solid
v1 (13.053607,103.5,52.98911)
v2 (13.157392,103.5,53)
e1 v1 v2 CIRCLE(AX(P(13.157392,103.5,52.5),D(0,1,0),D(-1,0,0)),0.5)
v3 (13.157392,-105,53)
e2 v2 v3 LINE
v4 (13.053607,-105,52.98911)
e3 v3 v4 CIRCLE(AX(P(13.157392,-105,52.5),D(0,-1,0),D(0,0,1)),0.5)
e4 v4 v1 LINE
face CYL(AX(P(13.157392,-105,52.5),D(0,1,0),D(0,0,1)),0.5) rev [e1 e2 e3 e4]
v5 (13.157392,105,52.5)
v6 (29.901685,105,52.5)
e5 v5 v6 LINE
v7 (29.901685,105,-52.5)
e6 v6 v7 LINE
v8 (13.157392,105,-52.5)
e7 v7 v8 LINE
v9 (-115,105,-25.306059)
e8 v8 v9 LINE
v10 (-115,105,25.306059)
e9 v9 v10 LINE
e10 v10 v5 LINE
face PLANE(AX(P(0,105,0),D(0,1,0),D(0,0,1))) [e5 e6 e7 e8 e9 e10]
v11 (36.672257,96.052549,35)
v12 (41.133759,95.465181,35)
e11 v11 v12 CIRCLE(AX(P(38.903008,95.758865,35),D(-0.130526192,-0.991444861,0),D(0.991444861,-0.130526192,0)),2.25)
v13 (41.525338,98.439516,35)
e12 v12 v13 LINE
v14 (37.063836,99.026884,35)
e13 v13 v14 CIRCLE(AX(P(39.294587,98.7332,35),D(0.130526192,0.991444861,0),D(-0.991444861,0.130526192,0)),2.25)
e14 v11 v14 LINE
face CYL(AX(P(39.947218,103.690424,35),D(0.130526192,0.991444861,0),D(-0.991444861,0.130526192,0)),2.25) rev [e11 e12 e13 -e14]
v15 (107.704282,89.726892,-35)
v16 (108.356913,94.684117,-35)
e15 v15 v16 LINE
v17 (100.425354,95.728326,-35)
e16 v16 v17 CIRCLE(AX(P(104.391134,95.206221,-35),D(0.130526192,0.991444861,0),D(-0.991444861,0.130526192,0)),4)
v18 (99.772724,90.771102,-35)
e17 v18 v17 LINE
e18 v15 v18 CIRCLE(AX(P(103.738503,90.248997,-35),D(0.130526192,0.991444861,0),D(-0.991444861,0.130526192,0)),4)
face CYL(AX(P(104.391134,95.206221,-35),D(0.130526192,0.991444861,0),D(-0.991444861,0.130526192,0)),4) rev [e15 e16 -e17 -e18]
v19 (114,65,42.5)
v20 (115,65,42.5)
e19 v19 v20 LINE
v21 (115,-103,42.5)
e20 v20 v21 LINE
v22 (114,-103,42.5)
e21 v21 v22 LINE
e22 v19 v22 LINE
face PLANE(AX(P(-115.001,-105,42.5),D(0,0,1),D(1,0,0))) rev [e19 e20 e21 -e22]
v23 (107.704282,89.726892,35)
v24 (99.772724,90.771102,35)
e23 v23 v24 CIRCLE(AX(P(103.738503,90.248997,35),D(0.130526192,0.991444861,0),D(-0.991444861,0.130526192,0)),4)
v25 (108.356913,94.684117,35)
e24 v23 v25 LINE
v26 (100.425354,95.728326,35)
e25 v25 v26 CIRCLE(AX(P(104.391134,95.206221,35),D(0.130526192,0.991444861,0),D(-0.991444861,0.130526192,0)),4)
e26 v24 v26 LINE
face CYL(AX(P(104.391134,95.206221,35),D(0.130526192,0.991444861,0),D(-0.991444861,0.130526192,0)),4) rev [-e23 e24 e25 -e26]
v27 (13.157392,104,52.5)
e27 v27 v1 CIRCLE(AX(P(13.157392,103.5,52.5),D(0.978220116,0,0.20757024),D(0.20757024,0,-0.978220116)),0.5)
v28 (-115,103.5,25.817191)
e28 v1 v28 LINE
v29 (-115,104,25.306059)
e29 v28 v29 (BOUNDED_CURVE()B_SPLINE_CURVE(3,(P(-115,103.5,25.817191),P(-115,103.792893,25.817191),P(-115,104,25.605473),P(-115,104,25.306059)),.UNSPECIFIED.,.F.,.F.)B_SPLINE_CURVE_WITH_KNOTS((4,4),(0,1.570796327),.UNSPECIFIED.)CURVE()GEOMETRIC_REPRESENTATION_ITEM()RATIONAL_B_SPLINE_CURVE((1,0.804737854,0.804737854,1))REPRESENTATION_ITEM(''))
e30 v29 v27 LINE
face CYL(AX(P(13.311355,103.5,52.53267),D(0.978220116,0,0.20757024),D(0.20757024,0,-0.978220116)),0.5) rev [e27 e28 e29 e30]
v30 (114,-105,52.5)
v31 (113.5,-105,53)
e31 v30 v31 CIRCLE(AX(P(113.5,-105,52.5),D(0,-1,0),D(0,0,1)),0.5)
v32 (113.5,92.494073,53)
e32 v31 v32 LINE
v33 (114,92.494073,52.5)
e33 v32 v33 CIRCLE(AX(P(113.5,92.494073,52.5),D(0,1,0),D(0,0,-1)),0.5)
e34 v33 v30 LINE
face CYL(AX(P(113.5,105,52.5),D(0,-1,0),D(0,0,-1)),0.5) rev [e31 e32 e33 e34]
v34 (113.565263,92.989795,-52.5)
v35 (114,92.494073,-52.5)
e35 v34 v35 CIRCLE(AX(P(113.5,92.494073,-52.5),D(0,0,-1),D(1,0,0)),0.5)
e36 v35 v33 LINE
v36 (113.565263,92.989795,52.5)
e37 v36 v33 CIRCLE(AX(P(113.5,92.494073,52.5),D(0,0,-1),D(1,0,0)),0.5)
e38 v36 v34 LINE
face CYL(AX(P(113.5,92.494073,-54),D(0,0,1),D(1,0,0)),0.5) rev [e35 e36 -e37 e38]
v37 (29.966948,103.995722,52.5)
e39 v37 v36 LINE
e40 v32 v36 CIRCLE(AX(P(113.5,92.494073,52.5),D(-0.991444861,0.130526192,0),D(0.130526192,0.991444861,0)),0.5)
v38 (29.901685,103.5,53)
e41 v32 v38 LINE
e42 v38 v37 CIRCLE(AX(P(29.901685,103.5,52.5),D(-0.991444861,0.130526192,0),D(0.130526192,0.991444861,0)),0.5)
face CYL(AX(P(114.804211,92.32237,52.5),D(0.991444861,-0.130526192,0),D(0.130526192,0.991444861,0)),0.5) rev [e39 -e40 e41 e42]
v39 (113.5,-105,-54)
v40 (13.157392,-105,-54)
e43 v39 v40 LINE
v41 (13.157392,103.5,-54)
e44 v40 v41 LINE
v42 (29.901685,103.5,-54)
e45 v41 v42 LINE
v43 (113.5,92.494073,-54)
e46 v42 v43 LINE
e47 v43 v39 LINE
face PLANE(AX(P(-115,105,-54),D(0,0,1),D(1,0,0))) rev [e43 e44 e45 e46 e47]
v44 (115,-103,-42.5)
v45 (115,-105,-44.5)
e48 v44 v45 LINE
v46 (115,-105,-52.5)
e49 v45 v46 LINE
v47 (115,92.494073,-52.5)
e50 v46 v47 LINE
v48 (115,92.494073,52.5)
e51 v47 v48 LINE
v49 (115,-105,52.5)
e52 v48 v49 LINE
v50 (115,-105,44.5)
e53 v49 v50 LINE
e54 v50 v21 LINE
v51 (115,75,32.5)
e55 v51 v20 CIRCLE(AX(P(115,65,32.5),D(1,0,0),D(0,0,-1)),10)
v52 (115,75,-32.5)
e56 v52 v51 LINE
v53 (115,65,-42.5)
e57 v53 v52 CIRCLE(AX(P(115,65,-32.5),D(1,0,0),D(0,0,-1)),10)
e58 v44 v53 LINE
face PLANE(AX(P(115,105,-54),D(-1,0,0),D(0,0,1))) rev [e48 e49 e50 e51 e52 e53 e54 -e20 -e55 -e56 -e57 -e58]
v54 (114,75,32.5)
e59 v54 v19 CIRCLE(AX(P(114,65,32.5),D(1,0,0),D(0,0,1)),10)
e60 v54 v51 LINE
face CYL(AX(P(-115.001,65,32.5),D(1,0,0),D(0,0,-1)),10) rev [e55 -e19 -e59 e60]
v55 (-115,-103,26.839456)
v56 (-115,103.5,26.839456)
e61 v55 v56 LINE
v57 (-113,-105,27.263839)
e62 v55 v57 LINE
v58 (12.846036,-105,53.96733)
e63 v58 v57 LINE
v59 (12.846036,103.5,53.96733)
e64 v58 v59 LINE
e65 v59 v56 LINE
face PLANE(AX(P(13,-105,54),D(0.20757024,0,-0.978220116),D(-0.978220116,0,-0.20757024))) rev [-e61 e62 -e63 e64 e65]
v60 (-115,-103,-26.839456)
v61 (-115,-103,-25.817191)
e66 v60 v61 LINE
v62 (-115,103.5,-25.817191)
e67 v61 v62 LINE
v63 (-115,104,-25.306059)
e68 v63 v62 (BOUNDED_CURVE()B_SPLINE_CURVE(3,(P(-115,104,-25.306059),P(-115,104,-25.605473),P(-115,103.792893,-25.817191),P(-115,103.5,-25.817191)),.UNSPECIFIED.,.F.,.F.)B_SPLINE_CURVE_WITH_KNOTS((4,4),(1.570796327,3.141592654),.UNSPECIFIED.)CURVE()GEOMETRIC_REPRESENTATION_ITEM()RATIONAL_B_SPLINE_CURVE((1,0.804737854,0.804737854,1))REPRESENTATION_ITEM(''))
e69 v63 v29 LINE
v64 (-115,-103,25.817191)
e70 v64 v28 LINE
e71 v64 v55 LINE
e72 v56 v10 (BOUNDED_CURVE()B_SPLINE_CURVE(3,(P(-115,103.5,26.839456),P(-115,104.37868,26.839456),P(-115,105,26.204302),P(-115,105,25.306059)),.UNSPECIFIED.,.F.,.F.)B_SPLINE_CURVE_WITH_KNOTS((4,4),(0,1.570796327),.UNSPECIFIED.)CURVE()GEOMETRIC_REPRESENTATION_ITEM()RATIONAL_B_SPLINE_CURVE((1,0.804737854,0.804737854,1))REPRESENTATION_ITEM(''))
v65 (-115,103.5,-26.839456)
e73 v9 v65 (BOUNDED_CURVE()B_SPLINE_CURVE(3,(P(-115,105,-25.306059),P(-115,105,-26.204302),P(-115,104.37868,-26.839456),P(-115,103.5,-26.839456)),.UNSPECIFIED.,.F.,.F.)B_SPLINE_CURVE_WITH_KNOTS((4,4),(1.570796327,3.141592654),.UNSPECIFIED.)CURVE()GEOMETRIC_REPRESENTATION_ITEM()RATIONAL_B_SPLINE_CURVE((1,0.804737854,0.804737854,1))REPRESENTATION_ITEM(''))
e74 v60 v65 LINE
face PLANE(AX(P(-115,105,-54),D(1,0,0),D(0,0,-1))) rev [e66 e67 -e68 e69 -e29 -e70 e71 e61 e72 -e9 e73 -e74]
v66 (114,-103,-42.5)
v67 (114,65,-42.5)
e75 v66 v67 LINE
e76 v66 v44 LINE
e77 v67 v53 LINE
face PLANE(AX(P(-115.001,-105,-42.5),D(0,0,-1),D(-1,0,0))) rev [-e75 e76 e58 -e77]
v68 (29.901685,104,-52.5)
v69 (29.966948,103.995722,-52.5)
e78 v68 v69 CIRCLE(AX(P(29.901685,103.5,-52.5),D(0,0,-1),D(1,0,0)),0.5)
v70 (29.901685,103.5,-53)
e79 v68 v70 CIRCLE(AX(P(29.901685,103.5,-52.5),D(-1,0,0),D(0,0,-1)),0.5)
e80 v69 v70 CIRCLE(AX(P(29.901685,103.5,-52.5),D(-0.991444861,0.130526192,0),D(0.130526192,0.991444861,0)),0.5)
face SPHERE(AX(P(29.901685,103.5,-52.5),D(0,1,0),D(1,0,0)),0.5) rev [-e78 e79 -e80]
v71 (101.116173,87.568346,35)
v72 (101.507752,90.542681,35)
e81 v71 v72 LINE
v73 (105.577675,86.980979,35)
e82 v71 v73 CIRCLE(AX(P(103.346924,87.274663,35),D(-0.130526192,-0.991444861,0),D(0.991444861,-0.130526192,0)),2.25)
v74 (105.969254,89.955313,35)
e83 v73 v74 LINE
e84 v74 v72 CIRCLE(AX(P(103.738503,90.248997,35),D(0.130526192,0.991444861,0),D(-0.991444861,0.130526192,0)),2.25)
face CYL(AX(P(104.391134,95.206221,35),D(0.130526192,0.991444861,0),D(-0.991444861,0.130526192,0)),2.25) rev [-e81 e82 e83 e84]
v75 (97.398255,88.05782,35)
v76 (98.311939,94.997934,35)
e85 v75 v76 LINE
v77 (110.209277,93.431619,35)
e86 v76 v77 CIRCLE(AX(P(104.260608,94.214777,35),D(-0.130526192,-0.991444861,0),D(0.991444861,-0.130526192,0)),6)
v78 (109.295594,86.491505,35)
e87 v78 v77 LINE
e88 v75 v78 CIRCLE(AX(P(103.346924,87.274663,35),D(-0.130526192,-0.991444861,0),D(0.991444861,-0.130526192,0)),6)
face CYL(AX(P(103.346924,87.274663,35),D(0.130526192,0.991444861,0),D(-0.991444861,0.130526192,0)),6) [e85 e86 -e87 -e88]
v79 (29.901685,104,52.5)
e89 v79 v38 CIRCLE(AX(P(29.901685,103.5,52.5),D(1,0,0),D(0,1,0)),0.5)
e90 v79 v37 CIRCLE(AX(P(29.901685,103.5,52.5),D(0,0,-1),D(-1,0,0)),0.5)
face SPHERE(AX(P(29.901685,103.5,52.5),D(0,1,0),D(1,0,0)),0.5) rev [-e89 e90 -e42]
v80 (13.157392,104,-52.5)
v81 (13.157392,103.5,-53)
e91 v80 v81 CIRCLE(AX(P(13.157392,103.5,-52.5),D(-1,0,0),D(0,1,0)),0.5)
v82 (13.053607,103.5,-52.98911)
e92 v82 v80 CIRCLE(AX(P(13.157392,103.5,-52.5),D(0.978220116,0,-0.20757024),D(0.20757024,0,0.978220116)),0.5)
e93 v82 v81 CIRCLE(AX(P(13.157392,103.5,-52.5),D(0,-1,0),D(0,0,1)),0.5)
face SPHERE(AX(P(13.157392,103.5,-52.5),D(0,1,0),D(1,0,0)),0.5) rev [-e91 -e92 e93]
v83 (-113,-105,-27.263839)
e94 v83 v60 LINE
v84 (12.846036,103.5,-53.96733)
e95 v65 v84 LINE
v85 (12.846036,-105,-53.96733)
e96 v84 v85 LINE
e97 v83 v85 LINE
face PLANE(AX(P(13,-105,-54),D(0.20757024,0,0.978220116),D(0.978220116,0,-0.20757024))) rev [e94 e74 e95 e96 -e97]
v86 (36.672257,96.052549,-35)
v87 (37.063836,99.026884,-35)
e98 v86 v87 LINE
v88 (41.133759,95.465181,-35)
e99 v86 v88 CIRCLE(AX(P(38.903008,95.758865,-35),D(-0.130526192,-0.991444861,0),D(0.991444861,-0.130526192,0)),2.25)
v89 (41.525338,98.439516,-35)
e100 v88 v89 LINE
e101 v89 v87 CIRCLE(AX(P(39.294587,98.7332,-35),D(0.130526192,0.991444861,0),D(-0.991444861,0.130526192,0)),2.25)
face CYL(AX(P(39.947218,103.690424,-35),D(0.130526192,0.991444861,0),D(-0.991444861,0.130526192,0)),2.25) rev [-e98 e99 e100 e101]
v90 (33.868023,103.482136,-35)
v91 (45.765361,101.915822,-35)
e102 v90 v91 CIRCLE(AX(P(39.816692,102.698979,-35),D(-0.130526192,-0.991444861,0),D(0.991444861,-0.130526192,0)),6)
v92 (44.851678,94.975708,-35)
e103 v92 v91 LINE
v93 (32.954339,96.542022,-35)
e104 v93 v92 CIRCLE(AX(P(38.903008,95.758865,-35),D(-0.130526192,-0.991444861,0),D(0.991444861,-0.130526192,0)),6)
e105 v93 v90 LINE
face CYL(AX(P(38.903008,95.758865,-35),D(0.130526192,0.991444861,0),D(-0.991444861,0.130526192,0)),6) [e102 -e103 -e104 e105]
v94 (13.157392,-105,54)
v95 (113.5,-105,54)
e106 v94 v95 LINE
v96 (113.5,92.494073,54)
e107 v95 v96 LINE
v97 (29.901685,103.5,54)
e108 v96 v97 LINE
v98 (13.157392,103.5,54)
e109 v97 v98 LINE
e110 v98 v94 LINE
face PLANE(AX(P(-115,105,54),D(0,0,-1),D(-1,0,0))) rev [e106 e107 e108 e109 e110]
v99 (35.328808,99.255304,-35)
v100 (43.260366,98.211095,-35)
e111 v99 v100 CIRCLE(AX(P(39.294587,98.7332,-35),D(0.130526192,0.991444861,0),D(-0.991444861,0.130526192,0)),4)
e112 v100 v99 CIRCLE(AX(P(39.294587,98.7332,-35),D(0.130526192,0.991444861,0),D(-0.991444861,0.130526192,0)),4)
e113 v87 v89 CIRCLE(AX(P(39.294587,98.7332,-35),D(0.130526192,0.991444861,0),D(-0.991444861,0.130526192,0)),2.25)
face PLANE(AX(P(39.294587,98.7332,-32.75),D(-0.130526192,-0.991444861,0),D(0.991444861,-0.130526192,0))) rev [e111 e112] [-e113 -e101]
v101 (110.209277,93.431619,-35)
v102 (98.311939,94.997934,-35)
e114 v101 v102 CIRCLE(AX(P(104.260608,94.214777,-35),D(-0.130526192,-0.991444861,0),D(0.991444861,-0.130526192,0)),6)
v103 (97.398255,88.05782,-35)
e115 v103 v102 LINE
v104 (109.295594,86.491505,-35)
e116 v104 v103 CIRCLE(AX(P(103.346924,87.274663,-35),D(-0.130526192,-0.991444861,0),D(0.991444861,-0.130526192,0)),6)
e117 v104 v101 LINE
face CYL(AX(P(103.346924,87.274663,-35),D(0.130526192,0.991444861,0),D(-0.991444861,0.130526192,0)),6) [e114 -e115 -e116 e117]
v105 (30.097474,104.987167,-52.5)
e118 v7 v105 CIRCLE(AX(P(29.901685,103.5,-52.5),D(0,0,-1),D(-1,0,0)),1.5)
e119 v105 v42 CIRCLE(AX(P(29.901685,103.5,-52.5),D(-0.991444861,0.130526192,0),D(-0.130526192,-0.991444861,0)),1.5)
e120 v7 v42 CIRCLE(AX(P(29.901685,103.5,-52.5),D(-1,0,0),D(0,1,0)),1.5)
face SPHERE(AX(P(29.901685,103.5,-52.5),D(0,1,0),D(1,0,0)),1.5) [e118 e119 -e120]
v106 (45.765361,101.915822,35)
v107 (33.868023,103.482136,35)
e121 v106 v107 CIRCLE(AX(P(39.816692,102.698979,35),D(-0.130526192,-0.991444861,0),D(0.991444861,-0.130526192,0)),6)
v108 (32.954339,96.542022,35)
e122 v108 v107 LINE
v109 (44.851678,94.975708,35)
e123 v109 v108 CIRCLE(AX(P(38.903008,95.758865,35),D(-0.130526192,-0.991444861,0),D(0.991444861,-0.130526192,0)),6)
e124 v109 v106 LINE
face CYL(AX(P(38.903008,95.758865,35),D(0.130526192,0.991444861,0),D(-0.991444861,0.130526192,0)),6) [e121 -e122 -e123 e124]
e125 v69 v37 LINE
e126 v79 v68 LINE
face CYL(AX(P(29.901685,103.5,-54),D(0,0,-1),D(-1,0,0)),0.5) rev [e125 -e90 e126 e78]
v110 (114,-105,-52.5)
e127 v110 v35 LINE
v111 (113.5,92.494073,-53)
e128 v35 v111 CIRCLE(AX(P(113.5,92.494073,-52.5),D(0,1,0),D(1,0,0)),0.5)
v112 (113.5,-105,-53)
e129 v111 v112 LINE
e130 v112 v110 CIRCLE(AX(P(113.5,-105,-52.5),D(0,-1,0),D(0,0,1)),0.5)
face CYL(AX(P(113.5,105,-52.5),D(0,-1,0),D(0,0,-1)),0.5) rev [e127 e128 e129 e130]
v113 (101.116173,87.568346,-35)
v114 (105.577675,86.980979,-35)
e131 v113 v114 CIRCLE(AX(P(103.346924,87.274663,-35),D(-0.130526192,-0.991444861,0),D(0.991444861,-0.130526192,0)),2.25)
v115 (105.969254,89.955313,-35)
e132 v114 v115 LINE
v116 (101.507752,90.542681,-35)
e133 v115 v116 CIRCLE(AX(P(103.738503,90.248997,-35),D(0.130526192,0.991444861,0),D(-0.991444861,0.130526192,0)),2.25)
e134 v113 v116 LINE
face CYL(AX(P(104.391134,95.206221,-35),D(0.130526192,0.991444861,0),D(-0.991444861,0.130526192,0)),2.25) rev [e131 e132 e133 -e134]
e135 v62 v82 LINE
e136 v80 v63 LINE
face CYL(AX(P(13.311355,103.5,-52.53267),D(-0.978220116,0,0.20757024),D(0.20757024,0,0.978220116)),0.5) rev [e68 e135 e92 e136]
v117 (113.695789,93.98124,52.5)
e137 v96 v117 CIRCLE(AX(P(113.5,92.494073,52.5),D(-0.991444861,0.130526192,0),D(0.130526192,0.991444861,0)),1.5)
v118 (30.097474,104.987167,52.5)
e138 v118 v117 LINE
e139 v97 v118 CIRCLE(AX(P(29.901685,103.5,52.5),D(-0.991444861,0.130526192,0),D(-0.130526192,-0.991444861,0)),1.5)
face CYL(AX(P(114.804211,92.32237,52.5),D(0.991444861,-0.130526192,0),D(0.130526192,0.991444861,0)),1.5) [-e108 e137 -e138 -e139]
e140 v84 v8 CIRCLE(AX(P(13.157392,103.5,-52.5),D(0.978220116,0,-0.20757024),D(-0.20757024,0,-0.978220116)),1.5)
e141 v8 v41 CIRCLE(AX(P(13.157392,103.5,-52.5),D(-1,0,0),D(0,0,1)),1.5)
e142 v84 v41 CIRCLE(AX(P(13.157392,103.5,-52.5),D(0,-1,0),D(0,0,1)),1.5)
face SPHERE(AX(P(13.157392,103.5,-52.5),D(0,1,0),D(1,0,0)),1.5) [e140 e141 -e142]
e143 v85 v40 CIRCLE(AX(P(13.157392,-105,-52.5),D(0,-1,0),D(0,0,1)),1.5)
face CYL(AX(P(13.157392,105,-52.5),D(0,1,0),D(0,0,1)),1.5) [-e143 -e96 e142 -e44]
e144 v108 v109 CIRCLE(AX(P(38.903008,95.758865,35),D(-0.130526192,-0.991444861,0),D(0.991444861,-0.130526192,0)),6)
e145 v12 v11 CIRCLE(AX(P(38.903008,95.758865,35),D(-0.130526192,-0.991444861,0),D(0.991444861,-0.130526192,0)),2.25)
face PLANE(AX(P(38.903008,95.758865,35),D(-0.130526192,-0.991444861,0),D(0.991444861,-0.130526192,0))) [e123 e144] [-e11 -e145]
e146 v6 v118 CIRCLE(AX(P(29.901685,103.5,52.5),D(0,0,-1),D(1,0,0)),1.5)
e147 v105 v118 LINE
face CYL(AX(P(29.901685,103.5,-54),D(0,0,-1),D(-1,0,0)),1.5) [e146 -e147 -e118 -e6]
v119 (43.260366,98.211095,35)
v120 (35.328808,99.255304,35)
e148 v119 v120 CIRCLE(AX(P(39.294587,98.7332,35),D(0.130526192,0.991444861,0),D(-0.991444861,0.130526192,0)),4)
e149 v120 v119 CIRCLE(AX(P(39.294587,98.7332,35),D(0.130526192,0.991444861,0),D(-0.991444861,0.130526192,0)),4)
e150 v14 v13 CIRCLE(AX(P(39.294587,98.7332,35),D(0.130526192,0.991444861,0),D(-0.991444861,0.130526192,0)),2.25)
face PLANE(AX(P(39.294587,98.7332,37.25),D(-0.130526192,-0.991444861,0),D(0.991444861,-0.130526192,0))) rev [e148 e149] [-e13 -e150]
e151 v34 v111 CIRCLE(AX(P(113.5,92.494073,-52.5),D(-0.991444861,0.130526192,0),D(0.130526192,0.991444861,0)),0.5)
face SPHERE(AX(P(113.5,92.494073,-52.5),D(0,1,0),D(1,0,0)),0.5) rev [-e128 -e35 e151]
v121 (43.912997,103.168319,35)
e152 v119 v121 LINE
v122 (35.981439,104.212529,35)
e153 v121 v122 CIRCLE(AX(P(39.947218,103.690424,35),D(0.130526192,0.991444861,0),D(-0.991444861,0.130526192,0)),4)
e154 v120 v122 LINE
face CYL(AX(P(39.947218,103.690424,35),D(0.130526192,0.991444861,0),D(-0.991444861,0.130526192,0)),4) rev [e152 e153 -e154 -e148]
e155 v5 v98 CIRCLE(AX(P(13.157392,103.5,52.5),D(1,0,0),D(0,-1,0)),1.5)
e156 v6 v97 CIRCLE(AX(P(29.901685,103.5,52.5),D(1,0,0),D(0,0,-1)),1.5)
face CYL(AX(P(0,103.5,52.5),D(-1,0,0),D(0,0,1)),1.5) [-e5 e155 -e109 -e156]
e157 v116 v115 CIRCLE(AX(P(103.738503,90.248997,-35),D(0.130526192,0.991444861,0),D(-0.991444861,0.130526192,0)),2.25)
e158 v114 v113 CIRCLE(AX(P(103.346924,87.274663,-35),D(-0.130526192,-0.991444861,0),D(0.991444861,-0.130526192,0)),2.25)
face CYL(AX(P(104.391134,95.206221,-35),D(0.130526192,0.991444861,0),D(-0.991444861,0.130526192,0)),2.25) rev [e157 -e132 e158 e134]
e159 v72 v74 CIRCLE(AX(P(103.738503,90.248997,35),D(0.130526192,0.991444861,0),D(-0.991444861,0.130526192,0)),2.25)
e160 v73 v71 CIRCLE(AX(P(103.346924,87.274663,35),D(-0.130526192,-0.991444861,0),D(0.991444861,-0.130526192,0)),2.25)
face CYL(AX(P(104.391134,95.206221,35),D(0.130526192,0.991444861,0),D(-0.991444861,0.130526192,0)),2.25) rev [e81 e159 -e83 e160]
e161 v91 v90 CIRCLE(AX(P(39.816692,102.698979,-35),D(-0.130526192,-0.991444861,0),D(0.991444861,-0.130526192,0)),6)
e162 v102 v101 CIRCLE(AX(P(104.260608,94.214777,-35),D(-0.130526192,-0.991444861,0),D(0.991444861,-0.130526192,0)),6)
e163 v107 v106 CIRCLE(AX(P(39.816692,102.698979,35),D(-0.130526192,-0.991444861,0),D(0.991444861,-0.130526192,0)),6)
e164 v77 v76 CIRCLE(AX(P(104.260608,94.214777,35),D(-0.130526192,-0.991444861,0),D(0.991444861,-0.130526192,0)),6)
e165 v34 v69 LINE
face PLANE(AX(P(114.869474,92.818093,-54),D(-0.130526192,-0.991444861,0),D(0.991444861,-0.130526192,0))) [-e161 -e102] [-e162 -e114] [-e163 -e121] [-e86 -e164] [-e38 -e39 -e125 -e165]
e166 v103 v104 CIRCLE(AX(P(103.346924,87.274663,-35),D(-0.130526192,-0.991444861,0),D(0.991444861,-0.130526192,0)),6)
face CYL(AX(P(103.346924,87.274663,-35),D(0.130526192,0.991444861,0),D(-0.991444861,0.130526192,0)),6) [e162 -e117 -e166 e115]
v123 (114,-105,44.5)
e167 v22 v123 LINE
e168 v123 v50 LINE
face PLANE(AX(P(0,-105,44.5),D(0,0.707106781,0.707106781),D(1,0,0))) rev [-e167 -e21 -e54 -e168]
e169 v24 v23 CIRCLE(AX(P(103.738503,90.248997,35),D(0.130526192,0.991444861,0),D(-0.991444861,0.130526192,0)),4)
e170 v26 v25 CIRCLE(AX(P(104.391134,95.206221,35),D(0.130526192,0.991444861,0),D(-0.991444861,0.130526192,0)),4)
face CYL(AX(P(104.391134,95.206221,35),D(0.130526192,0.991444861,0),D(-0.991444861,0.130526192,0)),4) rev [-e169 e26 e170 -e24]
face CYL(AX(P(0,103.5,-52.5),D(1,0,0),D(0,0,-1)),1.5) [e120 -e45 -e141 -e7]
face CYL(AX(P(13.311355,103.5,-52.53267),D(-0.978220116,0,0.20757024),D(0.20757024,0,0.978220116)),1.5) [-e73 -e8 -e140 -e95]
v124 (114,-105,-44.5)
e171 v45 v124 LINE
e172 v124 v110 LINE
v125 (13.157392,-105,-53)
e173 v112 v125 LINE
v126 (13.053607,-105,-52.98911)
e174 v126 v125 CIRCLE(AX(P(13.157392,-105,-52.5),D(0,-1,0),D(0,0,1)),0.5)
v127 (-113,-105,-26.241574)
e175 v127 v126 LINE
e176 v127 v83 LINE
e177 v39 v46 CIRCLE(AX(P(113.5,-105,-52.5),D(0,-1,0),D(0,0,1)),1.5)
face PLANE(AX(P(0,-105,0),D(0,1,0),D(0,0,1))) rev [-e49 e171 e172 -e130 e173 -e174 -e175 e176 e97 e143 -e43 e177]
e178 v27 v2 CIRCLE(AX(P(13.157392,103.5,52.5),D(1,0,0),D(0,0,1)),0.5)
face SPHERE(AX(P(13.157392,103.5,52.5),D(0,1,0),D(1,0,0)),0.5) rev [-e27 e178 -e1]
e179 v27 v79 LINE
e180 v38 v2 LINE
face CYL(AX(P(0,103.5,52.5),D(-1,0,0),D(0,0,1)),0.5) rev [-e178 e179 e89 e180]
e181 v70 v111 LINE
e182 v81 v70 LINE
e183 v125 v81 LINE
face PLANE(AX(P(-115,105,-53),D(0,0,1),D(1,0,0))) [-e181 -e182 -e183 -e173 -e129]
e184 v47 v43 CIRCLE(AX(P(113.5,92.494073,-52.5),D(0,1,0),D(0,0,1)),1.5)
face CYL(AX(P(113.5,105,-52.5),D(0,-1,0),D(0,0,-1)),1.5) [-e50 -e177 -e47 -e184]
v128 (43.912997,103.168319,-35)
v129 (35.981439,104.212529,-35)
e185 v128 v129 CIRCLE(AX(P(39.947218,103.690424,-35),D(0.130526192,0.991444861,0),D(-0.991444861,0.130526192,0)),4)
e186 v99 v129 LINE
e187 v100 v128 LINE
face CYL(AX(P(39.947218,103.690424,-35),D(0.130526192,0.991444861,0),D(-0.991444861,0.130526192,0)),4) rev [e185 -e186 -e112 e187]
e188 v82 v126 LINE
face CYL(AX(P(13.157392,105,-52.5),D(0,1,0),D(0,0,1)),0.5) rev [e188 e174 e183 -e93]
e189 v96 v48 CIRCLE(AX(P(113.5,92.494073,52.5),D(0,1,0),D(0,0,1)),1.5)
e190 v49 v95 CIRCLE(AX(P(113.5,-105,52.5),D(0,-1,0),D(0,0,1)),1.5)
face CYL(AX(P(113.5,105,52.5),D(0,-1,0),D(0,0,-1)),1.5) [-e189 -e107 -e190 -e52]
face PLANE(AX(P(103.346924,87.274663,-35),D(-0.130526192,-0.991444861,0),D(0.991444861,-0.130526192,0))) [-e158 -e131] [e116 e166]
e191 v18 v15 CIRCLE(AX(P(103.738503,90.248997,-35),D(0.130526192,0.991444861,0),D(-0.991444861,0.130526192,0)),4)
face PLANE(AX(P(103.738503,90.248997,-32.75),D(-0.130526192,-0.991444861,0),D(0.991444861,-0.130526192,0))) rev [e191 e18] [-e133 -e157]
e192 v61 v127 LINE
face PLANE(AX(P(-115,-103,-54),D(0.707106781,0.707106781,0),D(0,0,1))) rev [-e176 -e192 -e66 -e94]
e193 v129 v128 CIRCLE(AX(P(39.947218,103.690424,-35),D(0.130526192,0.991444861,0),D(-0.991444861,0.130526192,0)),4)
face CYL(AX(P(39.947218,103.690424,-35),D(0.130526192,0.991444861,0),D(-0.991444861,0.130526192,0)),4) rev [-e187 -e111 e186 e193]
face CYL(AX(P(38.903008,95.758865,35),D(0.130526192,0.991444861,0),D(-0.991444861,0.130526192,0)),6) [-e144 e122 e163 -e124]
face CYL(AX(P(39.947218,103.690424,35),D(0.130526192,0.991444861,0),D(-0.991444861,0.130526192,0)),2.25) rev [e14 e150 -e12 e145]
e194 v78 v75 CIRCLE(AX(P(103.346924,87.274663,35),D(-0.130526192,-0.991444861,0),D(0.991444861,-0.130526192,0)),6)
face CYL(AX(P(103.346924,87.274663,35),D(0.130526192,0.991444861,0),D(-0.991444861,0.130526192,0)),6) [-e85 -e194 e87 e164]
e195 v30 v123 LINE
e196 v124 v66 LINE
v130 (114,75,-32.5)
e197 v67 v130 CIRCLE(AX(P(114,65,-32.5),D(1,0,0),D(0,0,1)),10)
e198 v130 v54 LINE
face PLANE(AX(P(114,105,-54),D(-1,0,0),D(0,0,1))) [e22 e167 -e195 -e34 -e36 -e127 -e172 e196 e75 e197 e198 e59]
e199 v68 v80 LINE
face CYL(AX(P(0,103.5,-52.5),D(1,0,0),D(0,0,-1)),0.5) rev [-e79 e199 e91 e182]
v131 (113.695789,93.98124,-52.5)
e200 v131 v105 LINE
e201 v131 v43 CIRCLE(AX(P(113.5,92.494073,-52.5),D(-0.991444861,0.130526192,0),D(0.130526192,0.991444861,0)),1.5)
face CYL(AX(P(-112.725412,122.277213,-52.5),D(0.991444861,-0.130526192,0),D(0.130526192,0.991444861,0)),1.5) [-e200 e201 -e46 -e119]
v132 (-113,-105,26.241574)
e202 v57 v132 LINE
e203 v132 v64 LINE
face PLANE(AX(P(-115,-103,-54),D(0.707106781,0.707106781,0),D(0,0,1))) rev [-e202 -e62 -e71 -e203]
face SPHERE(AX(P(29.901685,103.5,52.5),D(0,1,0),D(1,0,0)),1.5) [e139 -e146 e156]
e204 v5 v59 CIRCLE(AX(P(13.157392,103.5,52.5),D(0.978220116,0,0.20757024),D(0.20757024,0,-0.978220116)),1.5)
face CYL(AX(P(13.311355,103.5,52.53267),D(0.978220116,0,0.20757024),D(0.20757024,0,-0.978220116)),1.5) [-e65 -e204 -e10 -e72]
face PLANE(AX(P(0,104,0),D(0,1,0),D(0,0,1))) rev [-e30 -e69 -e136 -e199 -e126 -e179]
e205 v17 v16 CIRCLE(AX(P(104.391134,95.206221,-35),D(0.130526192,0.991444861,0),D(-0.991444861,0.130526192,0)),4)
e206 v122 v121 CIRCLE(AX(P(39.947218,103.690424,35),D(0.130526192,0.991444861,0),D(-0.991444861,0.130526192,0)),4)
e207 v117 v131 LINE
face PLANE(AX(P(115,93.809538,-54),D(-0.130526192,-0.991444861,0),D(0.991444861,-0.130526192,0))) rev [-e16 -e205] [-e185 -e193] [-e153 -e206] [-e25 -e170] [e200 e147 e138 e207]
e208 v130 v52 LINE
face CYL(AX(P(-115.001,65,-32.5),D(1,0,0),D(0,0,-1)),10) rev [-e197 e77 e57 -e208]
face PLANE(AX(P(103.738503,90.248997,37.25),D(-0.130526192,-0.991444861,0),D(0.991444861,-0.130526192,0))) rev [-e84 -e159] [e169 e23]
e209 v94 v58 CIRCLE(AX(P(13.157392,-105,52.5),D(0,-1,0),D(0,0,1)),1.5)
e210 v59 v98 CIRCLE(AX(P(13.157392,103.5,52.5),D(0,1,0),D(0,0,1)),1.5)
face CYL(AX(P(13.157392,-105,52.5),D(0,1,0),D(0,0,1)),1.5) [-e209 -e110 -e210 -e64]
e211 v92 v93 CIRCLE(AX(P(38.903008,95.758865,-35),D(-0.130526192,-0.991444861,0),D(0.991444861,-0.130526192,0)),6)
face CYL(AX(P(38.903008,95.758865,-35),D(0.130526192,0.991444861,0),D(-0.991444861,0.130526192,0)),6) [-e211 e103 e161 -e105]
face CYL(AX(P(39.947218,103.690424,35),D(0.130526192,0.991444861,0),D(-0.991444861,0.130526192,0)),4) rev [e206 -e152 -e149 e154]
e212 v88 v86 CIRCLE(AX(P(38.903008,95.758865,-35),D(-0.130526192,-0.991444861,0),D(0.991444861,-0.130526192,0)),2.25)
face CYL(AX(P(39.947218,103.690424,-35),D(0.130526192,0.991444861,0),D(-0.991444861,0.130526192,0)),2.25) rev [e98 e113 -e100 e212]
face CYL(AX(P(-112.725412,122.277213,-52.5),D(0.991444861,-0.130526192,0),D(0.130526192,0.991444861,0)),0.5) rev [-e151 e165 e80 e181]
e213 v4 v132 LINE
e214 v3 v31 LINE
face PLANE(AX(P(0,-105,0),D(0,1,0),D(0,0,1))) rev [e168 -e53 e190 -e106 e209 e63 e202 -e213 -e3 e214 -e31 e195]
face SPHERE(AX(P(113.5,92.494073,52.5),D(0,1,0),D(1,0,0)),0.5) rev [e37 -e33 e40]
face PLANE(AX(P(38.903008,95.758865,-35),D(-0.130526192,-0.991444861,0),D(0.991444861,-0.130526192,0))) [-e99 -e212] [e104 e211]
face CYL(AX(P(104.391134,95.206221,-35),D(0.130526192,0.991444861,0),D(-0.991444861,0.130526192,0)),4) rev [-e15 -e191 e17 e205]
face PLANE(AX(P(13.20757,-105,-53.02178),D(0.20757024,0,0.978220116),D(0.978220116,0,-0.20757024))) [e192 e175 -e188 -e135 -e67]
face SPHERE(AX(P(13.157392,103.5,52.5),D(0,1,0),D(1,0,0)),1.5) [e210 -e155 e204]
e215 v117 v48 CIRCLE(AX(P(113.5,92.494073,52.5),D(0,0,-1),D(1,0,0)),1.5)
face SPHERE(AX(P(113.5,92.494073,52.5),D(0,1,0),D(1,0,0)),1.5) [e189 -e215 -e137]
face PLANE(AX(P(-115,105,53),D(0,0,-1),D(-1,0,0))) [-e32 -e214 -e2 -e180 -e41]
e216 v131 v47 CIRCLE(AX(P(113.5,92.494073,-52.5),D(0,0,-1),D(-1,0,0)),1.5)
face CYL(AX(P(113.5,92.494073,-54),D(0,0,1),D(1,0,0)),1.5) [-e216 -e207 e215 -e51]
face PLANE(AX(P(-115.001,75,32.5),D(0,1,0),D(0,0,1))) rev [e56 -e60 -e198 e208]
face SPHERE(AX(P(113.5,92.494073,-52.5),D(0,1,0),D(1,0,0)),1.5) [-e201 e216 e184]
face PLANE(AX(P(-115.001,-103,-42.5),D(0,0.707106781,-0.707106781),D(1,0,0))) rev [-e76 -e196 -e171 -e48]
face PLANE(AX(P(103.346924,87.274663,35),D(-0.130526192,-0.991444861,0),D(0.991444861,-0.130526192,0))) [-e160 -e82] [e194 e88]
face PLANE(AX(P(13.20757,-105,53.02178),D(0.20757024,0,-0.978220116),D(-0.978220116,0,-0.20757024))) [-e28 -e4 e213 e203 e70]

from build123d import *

# Parameters (mm, degrees)
SKETCH1_W                                            = 230
SKETCH1_H                                            = 108
BOSS_EXTRUDE1_DEPTH                                  = 105
CUT_EXTRUDE1_DEPTH                                   = 246.440420469
CUT_EXTRUDE2_DEPTH                                   = 190.509894201
FILLET1_R                                            = 1.5
SHELL1_T                                             = -1
SKETCH4_R                                            = 6
BOSS_EXTRUDE2_DEPTH                                  = 7
HOLE_SIZE_PER_SOCKET_HEAD_CAP_SCREW_TYPE_D           = 4.5
HOLE_SIZE_PER_SOCKET_HEAD_CAP_SCREW_TYPE_CBORE_D     = 8
HOLE_SIZE_PER_SOCKET_HEAD_CAP_SCREW_TYPE_CBORE_DEPTH = 5
CUT_EXTRUDE3_REACH                                   = 260.536
CHAMFER1_SIZE                                        = 2


with BuildPart() as part:
    # Sketch1 → Boss-Extrude1 (new, symmetric)
    with BuildSketch(Plane(origin=(0, 0, 0), x_dir=(1, 0, 0), z_dir=(0, 1, 0))):
        Rectangle(SKETCH1_W, SKETCH1_H)
    extrude(amount=BOSS_EXTRUDE1_DEPTH, both=True)

    # Sketch2 → Cut-Extrude1 (cut, through all)
    with BuildSketch(Plane(origin=(0, 105, 0), x_dir=(1, 0, 0), z_dir=(0, 1, 0))):
        Polygon((-115, 26.839455747), (-115, 54), (13, 54), align=None)
        Polygon((-115, -26.839455747), (-115, -54), (13, -54), align=None)
    extrude(amount=-CUT_EXTRUDE1_DEPTH, mode=Mode.SUBTRACT)

    # Sketch3 → Cut-Extrude2 (cut, through all)
    with BuildSketch(Plane.XY.offset(54)):
        Polygon((30, 105), (115, 105), (115, 93.809537705), align=None)
    extrude(amount=-CUT_EXTRUDE2_DEPTH, mode=Mode.SUBTRACT)

    # Fillet1
    fillet1_edges = [part.edges().sort_by_distance(p)[0] for p in [
        (13, 0, -54),
        (-51, 105, -40.419727874),
        (21.5, 105, 54),
        (13, 0, 54),
        (-51, 105, 40.419727874),
        (21.5, 105, -54),
        (115, -5.595231147, 54),
        (115, -5.595231147, -54),
        (72.5, 99.404768853, -54),
        (115, 93.809537705, 0),
        (30, 105, 0),
        (72.5, 99.404768853, 54),
    ]]
    fillet(fillet1_edges, radius=FILLET1_R)

    # Shell1
    shell1_openings = [part.faces().sort_by_distance(p)[0] for p in [
        (11.766407096, -105, 0),
        (-115, -0.009166967, 0),
    ]]
    offset(amount=SHELL1_T, openings=shell1_openings, kind=Kind.INTERSECTION)

    # Sketch4 → Boss-Extrude2 (add)
    with BuildSketch(Plane(origin=(13.968586281, 106.101946695, 0), x_dir=(0.9914448613738114, -0.1305261922200448, 0), z_dir=(-0.1305261922200448, -0.9914448613738114, 0))):
        with Locations((26.071147756, 35)):
            Circle(SKETCH4_R)
        with Locations((26.071147756, -35)):
            Circle(SKETCH4_R)
        with Locations((91.071147756, -35)):
            Circle(SKETCH4_R)
        with Locations((91.071147756, 35)):
            Circle(SKETCH4_R)
    extrude(amount=BOSS_EXTRUDE2_DEPTH)

    # Hole size per socket head cap screw type1 (through all)
    with Locations(Plane(origin=(14.099112474, 107.093391557, 0), x_dir=(0.9914448613738114, -0.1305261922200448, 0), z_dir=(0.1305261922200448, 0.9914448613738114, 0))):
        with Locations((26.071147756, 35), (91.071147756, 35), (91.071147756, -35), (26.071147756, -35)):
            CounterBoreHole(HOLE_SIZE_PER_SOCKET_HEAD_CAP_SCREW_TYPE_D / 2, HOLE_SIZE_PER_SOCKET_HEAD_CAP_SCREW_TYPE_CBORE_D / 2, HOLE_SIZE_PER_SOCKET_HEAD_CAP_SCREW_TYPE_CBORE_DEPTH)

    # Sketch7 → Cut-Extrude3 (cut, up to next)
    with BuildSketch(Plane(origin=(115, 0, 0), x_dir=(0, 0, -1), z_dir=(1, 0, 0)), mode=Mode.PRIVATE) as cut_extrude3_sk1:
        with BuildLine():
            Line((-42.5, -105), (42.5, -105))
            Line((42.5, -105), (42.5, 65))
            ThreePointArc((42.5, 65), (39.571067812, 72.071067812), (32.5, 75))
            Line((32.5, 75), (-32.5, 75))
            ThreePointArc((-32.5, 75), (-39.571067812, 72.071067812), (-42.5, 65))
            Line((-42.5, 65), (-42.5, -105))
        make_face()
    cut_extrude3_tool1 = extrude(cut_extrude3_sk1.sketch, amount=-CUT_EXTRUDE3_REACH, mode=Mode.PRIVATE) & part.part
    add(cut_extrude3_tool1.solids().sort_by_distance((115, -15.246899, 0))[0], mode=Mode.SUBTRACT)

    # Chamfer1
    chamfer1_edges = [part.edges().sort_by_distance(p)[0] for p in [
        (-115, -105, -26.328323343),
        (114.5, -105, 42.5),
        (114.5, -105, -42.5),
        (-115, -105, 26.328323343),
    ]]
    chamfer(chamfer1_edges, length=CHAMFER1_SIZE)


solid = part.part
